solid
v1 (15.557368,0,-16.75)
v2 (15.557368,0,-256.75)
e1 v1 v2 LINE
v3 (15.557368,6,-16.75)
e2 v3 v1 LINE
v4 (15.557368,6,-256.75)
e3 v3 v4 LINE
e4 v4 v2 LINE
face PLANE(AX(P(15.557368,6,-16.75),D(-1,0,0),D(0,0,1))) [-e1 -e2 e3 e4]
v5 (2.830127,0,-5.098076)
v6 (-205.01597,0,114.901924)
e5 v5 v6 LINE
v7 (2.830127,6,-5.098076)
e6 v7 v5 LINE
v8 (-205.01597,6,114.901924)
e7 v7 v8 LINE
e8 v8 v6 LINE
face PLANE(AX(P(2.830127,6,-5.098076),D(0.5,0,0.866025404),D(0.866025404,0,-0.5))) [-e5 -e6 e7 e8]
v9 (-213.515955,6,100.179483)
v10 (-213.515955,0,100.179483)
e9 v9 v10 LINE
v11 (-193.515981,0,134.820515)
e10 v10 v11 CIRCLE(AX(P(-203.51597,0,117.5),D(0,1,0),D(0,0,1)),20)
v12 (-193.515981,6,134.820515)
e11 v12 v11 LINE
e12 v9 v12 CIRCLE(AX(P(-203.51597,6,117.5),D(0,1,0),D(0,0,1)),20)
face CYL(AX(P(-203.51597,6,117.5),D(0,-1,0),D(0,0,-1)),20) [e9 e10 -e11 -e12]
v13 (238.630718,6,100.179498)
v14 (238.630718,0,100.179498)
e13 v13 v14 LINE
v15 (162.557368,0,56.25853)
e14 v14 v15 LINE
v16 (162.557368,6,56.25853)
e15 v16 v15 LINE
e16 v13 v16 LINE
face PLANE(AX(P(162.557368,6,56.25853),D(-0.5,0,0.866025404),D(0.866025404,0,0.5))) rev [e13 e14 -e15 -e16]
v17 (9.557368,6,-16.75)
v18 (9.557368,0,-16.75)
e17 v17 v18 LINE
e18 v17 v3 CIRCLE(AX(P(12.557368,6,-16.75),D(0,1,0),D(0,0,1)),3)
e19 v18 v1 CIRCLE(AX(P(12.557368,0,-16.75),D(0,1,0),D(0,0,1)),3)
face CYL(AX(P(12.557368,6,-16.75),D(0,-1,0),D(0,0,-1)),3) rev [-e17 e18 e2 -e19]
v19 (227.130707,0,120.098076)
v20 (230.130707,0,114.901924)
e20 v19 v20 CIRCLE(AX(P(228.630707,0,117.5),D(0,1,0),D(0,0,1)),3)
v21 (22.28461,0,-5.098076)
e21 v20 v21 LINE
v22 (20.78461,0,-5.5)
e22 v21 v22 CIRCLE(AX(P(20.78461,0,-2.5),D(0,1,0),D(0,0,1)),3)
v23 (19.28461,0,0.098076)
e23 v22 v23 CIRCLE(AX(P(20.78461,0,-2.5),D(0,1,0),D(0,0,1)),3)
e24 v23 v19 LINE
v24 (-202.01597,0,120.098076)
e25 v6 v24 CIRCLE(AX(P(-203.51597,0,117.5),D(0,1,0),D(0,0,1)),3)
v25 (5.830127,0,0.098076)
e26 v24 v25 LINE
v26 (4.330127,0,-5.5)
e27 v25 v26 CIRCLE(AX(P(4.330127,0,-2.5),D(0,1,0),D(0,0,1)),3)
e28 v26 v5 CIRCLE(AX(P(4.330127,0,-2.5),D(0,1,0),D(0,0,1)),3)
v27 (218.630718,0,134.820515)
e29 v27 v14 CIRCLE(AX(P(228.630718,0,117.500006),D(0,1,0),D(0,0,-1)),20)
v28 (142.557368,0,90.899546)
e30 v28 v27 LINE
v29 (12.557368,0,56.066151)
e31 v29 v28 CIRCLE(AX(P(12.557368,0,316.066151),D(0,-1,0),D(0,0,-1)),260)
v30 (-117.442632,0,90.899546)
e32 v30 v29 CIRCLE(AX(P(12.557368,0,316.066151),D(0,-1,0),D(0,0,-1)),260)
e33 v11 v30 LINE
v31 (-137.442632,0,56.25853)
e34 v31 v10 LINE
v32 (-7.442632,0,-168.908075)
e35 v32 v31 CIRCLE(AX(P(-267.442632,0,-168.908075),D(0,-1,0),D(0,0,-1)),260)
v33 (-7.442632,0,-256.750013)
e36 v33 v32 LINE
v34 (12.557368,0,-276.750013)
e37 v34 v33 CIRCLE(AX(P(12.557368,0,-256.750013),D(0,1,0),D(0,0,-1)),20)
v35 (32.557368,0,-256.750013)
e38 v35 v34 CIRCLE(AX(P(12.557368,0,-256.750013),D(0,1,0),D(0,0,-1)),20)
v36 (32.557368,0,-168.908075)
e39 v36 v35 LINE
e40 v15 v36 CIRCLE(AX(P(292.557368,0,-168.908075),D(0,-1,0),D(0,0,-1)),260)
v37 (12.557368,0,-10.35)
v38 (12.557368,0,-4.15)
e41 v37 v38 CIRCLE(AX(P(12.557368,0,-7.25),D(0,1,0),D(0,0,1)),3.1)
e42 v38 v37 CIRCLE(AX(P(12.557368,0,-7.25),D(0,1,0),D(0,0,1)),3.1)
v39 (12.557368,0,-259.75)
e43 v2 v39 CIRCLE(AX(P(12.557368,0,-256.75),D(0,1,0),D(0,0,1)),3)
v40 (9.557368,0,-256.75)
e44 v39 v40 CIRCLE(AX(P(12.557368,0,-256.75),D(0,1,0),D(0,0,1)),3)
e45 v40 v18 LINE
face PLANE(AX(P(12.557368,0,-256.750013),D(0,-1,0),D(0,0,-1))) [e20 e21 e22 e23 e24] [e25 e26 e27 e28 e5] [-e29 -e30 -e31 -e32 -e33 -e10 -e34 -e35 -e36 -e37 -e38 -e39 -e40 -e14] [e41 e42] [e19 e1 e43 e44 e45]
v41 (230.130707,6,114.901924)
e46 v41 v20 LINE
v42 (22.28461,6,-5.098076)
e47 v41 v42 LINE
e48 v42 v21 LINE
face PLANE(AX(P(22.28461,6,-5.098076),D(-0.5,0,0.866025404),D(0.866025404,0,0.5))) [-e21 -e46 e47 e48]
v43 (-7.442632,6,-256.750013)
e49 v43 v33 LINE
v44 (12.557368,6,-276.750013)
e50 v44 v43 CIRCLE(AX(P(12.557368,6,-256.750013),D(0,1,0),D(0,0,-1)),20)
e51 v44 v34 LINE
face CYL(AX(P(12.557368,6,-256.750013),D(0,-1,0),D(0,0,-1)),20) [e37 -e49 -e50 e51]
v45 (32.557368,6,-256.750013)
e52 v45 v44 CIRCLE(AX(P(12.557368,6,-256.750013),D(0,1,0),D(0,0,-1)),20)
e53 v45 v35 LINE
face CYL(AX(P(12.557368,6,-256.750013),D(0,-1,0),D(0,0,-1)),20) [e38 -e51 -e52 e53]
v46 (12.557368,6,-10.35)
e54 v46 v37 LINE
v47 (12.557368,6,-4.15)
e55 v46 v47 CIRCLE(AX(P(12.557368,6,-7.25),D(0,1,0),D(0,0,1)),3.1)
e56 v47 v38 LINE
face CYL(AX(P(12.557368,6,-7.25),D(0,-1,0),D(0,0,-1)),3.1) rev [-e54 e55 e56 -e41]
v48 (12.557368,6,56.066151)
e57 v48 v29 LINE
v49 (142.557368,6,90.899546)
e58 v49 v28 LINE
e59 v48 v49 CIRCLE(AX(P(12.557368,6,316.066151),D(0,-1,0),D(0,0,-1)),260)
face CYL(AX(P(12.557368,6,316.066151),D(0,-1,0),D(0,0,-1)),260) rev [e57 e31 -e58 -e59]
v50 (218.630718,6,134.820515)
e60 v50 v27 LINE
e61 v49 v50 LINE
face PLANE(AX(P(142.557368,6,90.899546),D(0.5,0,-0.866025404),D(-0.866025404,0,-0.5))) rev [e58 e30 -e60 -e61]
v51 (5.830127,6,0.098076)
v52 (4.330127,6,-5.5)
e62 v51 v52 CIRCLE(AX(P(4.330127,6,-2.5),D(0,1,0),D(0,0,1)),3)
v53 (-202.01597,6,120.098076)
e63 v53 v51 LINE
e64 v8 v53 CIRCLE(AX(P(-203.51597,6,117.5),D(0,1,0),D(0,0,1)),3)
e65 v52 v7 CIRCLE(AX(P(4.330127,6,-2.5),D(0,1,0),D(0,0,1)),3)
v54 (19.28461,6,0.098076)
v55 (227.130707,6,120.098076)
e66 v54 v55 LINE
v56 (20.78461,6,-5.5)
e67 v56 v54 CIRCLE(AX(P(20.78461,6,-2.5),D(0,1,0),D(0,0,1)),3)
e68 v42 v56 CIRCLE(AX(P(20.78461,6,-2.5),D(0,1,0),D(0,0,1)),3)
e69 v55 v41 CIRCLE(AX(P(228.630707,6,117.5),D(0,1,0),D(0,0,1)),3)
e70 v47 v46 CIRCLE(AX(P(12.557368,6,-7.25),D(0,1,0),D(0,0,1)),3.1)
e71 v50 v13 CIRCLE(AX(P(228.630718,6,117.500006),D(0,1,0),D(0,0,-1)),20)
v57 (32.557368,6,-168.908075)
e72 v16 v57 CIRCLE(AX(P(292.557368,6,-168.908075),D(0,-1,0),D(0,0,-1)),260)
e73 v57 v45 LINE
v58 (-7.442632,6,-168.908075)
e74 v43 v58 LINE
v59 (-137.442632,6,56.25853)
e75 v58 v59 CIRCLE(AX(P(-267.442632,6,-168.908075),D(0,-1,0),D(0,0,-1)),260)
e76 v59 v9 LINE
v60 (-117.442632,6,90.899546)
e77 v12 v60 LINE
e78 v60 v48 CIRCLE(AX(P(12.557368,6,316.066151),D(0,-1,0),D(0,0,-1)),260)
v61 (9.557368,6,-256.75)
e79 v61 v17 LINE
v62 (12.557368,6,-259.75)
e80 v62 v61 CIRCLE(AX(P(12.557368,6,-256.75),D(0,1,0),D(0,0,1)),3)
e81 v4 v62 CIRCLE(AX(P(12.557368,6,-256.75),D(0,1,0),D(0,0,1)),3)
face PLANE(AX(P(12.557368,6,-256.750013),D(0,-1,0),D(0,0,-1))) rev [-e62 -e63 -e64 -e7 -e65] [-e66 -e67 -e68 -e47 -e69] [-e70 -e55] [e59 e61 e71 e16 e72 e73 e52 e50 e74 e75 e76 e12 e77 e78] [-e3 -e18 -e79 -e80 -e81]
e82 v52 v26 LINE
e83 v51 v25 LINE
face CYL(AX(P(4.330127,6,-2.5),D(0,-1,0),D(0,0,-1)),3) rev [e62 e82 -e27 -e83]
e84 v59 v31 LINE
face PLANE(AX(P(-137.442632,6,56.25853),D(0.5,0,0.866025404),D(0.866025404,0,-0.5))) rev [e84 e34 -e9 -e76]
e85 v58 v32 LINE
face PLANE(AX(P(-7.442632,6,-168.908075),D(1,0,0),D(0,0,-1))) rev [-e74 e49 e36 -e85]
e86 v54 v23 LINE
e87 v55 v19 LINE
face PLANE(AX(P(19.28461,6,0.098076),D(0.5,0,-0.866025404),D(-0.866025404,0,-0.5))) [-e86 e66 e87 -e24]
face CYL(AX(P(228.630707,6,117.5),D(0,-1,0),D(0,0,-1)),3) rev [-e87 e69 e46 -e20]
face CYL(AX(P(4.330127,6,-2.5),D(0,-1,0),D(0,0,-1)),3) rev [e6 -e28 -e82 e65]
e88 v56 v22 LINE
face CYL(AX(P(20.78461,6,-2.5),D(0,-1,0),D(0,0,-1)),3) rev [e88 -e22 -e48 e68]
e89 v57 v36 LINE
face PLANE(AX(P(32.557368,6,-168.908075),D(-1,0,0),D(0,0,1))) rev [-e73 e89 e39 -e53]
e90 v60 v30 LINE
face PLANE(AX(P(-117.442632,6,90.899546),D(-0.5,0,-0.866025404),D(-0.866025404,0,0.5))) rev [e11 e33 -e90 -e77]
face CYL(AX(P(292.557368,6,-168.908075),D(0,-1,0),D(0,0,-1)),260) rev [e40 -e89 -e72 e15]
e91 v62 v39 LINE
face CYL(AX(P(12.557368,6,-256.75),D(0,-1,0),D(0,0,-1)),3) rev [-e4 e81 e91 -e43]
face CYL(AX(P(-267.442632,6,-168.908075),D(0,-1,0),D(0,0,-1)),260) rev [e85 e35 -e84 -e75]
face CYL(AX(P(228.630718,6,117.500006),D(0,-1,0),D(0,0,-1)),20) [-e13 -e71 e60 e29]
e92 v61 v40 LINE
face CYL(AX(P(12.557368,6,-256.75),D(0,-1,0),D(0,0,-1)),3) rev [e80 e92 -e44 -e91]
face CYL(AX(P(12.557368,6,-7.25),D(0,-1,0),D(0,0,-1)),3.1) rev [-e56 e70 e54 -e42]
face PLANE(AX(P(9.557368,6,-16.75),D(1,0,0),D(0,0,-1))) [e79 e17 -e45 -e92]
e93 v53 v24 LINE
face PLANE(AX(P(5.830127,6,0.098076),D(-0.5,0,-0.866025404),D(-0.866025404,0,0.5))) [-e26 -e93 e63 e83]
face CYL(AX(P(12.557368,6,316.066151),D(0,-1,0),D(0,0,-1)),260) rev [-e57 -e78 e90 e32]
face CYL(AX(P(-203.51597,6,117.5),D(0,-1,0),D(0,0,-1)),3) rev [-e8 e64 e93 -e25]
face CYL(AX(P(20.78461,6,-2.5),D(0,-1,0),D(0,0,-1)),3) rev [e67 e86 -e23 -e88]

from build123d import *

# Parameters (mm, degrees)
SKETCH1_R           = 3.1
BOSS_EXTRUDE2_DEPTH = 6


with BuildPart() as part:
    # Sketch1 → Boss-Extrude2 (new body)
    with BuildSketch(Plane(origin=(0, 0, 0), x_dir=(1, 0, 0), z_dir=(0, 1, 0))):
        with BuildLine():
            Line((-7.442631645, 168.908075373), (-7.442631645, 256.750012922))
            ThreePointArc((-7.442631645, 256.750012922), (12.557368355, 276.750012922), (32.557368355, 256.750012922))
            Line((32.557368355, 256.750012922), (32.557368355, 168.908075373))
            ThreePointArc((32.557368355, 168.908075373), (67.390763371, 38.908075373), (162.557368355, -56.258529611))
            Line((162.557368355, -56.258529611), (238.63071779, -100.179498385))
            ThreePointArc((238.63071779, -100.179498385), (245.951225865, -127.500006461), (218.63071779, -134.820514537))
            Line((218.63071779, -134.820514537), (142.557368355, -90.899545762))
            ThreePointArc((142.557368355, -90.899545762), (12.557368355, -56.066150746), (-117.442631645, -90.899545762))
            Line((-117.442631645, -90.899545762), (-193.51598108, -134.820514537))
            ThreePointArc((-193.51598108, -134.820514537), (-220.836485566, -127.499986835), (-213.515954749, -100.179483183))
            Line((-213.515954749, -100.179483183), (-137.442631645, -56.258529611))
            ThreePointArc((-137.442631645, -56.258529611), (-42.276026661, 38.908075373), (-7.442631645, 168.908075373))
        make_face()
        with Locations(Location((12.557368355, 7.25, 0), (0, 0, 270))):
            Circle(SKETCH1_R, mode=Mode.SUBTRACT)
        with BuildLine():
            Line((5.830127019, -0.098076211), (-202.015969889, -120.098076211))
            ThreePointArc((-202.015969889, -120.098076211), (-206.114046101, -119), (-205.015969889, -114.901923789))
            Line((-205.015969889, -114.901923789), (2.830127019, 5.098076211))
            ThreePointArc((2.830127019, 5.098076211), (6.92820323, 4), (5.830127019, -0.098076211))
        make_face(mode=Mode.SUBTRACT)
        with BuildLine():
            Line((22.284609691, 5.098076211), (230.130706599, -114.901923789))
            ThreePointArc((230.130706599, -114.901923789), (231.22878281, -119), (227.130706599, -120.098076211))
            Line((227.130706599, -120.098076211), (19.284609691, -0.098076211))
            ThreePointArc((19.284609691, -0.098076211), (18.186533479, 4), (22.284609691, 5.098076211))
        make_face(mode=Mode.SUBTRACT)
        with BuildLine():
            Line((9.557368355, 16.75), (9.557368355, 256.75))
            ThreePointArc((9.557368355, 256.75), (12.557368355, 259.75), (15.557368355, 256.75))
            Line((15.557368355, 256.75), (15.557368355, 16.75))
            ThreePointArc((15.557368355, 16.75), (12.557368355, 13.75), (9.557368355, 16.75))
        make_face(mode=Mode.SUBTRACT)
    extrude(amount=BOSS_EXTRUDE2_DEPTH)


solid = part.part
